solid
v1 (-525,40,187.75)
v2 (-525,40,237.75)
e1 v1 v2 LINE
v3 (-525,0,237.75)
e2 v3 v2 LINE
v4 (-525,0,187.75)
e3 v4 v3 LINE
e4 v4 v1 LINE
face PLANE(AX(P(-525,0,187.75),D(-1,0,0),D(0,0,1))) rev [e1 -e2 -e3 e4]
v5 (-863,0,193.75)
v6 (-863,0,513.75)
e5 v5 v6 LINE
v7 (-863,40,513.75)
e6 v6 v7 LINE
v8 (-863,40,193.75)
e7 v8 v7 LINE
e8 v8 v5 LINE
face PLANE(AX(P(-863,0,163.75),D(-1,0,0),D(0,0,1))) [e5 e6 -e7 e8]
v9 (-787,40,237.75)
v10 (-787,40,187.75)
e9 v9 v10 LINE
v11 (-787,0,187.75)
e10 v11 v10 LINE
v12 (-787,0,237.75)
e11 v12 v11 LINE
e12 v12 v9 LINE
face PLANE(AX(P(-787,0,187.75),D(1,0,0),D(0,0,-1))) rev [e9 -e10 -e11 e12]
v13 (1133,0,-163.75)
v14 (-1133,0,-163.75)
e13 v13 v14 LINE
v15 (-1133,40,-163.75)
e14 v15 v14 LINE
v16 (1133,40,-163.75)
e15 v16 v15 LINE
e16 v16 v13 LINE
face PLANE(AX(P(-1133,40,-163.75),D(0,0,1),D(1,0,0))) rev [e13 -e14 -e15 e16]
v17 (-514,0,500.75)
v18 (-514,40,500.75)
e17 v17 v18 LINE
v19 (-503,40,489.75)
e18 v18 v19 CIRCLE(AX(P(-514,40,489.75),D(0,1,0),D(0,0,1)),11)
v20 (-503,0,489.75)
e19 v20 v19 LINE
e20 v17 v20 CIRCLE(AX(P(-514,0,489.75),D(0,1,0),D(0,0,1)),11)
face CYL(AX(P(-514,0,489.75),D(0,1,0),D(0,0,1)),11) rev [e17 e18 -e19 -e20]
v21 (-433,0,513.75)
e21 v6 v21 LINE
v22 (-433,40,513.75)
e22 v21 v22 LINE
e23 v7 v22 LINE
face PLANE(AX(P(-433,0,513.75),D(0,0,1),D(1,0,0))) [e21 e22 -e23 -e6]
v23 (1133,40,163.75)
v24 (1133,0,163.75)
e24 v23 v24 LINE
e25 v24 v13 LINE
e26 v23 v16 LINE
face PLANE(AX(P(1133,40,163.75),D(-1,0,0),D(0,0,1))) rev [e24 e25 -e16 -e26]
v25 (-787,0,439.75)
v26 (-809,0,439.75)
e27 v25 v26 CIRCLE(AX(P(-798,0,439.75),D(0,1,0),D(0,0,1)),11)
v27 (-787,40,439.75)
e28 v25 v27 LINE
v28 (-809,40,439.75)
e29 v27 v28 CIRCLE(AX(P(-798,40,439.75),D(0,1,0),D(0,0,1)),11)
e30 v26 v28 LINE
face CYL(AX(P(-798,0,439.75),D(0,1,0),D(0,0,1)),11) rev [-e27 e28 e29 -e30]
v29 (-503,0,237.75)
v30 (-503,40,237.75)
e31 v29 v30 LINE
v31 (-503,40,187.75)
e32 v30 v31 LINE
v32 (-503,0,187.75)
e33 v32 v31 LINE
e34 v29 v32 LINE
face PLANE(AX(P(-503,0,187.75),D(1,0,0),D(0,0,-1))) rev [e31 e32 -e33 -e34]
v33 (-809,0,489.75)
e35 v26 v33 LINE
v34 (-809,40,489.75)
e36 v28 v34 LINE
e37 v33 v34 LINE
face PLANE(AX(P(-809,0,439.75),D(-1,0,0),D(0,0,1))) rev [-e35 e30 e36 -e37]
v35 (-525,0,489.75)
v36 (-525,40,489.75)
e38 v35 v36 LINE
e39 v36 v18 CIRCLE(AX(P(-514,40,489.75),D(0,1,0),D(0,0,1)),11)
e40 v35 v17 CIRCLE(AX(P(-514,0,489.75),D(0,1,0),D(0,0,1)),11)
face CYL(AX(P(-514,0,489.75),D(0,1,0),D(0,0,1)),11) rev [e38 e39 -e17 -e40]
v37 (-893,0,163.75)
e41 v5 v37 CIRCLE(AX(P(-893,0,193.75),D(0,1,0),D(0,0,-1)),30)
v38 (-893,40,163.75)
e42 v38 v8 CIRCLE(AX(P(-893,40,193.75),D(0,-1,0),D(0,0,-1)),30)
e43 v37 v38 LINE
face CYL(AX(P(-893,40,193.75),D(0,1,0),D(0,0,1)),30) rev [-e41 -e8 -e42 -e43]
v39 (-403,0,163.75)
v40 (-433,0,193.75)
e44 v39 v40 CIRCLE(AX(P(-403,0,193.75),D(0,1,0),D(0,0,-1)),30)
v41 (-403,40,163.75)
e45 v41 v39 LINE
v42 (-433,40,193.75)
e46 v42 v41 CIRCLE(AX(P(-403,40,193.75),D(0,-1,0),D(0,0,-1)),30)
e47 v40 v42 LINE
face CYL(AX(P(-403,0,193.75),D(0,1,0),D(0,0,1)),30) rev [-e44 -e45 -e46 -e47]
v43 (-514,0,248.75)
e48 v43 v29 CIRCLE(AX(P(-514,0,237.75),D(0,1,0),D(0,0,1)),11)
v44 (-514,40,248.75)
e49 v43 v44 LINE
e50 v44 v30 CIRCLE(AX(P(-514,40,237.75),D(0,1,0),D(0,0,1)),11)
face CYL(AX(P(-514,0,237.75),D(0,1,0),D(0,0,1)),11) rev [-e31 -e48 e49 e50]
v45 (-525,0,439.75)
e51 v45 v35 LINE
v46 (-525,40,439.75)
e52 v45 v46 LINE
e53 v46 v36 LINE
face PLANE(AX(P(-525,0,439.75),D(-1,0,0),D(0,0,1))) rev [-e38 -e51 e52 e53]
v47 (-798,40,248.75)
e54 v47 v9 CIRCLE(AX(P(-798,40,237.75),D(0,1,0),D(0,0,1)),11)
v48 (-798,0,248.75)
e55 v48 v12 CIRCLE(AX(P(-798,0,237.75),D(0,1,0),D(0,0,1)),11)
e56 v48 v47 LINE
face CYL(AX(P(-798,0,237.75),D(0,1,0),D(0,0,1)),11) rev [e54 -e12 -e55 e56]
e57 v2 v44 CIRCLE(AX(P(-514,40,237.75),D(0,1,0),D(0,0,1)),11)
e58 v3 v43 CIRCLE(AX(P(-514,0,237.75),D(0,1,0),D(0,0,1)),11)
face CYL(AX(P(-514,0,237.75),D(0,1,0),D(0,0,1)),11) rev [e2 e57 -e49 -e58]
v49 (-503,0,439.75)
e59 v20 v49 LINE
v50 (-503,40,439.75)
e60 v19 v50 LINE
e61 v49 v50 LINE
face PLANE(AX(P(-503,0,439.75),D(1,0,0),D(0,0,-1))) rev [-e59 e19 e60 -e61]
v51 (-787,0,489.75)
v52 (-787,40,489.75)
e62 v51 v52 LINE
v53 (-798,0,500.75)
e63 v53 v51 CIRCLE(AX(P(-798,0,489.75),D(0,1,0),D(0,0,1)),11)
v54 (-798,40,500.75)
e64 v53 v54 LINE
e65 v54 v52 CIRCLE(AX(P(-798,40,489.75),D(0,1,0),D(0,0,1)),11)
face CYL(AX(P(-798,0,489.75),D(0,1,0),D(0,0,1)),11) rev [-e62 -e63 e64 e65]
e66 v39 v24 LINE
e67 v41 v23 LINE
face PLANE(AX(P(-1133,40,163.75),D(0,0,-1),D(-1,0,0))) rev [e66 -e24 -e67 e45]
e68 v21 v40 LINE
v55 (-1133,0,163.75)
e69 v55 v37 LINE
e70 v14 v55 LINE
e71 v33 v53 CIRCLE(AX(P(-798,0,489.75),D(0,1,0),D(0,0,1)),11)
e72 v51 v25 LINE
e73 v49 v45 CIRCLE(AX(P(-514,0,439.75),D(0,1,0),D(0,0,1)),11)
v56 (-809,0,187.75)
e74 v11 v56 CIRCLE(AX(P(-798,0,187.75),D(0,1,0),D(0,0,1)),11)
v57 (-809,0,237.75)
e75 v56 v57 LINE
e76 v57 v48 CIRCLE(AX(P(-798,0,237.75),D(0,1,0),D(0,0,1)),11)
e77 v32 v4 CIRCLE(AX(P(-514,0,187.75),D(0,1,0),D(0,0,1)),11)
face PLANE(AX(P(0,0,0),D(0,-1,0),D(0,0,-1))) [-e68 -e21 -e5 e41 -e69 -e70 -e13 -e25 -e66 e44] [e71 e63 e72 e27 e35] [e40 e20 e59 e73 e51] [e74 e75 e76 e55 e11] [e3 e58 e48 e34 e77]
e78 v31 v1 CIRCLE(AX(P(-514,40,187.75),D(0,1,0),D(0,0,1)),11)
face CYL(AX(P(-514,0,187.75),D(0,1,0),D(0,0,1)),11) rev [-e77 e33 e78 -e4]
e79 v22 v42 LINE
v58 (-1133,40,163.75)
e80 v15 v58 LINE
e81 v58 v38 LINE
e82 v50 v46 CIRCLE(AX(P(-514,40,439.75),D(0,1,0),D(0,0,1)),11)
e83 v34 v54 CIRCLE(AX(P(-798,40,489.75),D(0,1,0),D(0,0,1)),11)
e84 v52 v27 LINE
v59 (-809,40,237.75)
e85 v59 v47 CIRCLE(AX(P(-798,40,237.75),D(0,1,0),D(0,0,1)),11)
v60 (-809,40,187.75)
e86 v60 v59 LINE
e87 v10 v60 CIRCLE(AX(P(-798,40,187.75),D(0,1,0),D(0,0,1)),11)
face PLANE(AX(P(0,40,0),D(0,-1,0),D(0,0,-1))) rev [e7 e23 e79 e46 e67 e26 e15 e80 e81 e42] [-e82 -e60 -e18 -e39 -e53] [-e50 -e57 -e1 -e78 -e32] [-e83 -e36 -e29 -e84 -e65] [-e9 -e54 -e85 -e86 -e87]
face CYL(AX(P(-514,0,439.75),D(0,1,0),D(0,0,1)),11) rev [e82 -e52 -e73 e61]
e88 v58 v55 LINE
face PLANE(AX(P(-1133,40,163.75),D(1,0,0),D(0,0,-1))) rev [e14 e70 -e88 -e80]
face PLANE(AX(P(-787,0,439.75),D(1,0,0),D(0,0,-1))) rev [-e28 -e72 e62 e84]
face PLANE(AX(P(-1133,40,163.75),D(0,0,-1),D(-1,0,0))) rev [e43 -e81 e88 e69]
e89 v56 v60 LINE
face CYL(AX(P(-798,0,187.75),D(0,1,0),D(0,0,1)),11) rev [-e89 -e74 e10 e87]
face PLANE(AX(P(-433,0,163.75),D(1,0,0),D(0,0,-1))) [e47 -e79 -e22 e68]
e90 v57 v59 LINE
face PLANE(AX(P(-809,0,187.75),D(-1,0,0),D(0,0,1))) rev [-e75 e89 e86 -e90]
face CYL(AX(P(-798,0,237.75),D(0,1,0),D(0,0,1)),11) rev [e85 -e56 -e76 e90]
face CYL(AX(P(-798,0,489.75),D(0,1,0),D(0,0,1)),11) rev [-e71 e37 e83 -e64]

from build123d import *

# Parameters (mm, degrees)
SKETCH_1_W          = 2266
SKETCH_1_H          = 327.5
EXTRUDE_1_DEPTH     = 40
SKETCH_2_W          = 430
SKETCH_2_H          = 350
EXTRUDE_2_DEPTH     = 40
CUT_EXTRUDE_1_DEPTH = 1245.67990363
FILLET_1_R          = 30


with BuildPart() as part:
    # 草图1 → 凸台-拉伸1 (new body)
    with BuildSketch(Plane(origin=(0, 0, 0), x_dir=(1, 0, 0), z_dir=(0, 1, 0))):
        Rectangle(SKETCH_1_W, SKETCH_1_H)
    extrude(amount=EXTRUDE_1_DEPTH)

    # 草图2 → 凸台-拉伸2 (add)
    with BuildSketch(Plane(origin=(0, 40, 0), x_dir=(1, 0, 0), z_dir=(0, 1, 0))):
        with Locations((-648, -338.75)):
            Rectangle(SKETCH_2_W, SKETCH_2_H)
    extrude(amount=-EXTRUDE_2_DEPTH)

    # 草图3 → 切除-拉伸1 (cut, through all)
    with BuildSketch(Plane(origin=(0, 40, 0), x_dir=(1, 0, 0), z_dir=(0, 1, 0))):
        with BuildLine():
            Line((-503, -187.75), (-503, -237.75))
            ThreePointArc((-503, -237.75), (-514, -248.75), (-525, -237.75))
            Line((-525, -237.75), (-525, -187.75))
            ThreePointArc((-525, -187.75), (-514, -176.75), (-503, -187.75))
        make_face()
        with BuildLine():
            Line((-787, -187.75), (-787, -237.75))
            ThreePointArc((-787, -237.75), (-798, -248.75), (-809, -237.75))
            Line((-809, -237.75), (-809, -187.75))
            ThreePointArc((-809, -187.75), (-798, -176.75), (-787, -187.75))
        make_face()
        with BuildLine():
            Line((-787, -439.75), (-787, -489.75))
            ThreePointArc((-787, -489.75), (-798, -500.75), (-809, -489.75))
            Line((-809, -489.75), (-809, -439.75))
            ThreePointArc((-809, -439.75), (-798, -428.75), (-787, -439.75))
        make_face()
        with BuildLine():
            Line((-503, -439.75), (-503, -489.75))
            ThreePointArc((-503, -489.75), (-514, -500.75), (-525, -489.75))
            Line((-525, -489.75), (-525, -439.75))
            ThreePointArc((-525, -439.75), (-514, -428.75), (-503, -439.75))
        make_face()
    extrude(amount=-CUT_EXTRUDE_1_DEPTH, mode=Mode.SUBTRACT)

    # 圆角1
    fillet_1_edges = [part.edges().sort_by_distance(p)[0] for p in [
        (-433, 20, 163.75),
        (-863, 20, 163.75),
    ]]
    fillet(fillet_1_edges, radius=FILLET_1_R)


solid = part.part
